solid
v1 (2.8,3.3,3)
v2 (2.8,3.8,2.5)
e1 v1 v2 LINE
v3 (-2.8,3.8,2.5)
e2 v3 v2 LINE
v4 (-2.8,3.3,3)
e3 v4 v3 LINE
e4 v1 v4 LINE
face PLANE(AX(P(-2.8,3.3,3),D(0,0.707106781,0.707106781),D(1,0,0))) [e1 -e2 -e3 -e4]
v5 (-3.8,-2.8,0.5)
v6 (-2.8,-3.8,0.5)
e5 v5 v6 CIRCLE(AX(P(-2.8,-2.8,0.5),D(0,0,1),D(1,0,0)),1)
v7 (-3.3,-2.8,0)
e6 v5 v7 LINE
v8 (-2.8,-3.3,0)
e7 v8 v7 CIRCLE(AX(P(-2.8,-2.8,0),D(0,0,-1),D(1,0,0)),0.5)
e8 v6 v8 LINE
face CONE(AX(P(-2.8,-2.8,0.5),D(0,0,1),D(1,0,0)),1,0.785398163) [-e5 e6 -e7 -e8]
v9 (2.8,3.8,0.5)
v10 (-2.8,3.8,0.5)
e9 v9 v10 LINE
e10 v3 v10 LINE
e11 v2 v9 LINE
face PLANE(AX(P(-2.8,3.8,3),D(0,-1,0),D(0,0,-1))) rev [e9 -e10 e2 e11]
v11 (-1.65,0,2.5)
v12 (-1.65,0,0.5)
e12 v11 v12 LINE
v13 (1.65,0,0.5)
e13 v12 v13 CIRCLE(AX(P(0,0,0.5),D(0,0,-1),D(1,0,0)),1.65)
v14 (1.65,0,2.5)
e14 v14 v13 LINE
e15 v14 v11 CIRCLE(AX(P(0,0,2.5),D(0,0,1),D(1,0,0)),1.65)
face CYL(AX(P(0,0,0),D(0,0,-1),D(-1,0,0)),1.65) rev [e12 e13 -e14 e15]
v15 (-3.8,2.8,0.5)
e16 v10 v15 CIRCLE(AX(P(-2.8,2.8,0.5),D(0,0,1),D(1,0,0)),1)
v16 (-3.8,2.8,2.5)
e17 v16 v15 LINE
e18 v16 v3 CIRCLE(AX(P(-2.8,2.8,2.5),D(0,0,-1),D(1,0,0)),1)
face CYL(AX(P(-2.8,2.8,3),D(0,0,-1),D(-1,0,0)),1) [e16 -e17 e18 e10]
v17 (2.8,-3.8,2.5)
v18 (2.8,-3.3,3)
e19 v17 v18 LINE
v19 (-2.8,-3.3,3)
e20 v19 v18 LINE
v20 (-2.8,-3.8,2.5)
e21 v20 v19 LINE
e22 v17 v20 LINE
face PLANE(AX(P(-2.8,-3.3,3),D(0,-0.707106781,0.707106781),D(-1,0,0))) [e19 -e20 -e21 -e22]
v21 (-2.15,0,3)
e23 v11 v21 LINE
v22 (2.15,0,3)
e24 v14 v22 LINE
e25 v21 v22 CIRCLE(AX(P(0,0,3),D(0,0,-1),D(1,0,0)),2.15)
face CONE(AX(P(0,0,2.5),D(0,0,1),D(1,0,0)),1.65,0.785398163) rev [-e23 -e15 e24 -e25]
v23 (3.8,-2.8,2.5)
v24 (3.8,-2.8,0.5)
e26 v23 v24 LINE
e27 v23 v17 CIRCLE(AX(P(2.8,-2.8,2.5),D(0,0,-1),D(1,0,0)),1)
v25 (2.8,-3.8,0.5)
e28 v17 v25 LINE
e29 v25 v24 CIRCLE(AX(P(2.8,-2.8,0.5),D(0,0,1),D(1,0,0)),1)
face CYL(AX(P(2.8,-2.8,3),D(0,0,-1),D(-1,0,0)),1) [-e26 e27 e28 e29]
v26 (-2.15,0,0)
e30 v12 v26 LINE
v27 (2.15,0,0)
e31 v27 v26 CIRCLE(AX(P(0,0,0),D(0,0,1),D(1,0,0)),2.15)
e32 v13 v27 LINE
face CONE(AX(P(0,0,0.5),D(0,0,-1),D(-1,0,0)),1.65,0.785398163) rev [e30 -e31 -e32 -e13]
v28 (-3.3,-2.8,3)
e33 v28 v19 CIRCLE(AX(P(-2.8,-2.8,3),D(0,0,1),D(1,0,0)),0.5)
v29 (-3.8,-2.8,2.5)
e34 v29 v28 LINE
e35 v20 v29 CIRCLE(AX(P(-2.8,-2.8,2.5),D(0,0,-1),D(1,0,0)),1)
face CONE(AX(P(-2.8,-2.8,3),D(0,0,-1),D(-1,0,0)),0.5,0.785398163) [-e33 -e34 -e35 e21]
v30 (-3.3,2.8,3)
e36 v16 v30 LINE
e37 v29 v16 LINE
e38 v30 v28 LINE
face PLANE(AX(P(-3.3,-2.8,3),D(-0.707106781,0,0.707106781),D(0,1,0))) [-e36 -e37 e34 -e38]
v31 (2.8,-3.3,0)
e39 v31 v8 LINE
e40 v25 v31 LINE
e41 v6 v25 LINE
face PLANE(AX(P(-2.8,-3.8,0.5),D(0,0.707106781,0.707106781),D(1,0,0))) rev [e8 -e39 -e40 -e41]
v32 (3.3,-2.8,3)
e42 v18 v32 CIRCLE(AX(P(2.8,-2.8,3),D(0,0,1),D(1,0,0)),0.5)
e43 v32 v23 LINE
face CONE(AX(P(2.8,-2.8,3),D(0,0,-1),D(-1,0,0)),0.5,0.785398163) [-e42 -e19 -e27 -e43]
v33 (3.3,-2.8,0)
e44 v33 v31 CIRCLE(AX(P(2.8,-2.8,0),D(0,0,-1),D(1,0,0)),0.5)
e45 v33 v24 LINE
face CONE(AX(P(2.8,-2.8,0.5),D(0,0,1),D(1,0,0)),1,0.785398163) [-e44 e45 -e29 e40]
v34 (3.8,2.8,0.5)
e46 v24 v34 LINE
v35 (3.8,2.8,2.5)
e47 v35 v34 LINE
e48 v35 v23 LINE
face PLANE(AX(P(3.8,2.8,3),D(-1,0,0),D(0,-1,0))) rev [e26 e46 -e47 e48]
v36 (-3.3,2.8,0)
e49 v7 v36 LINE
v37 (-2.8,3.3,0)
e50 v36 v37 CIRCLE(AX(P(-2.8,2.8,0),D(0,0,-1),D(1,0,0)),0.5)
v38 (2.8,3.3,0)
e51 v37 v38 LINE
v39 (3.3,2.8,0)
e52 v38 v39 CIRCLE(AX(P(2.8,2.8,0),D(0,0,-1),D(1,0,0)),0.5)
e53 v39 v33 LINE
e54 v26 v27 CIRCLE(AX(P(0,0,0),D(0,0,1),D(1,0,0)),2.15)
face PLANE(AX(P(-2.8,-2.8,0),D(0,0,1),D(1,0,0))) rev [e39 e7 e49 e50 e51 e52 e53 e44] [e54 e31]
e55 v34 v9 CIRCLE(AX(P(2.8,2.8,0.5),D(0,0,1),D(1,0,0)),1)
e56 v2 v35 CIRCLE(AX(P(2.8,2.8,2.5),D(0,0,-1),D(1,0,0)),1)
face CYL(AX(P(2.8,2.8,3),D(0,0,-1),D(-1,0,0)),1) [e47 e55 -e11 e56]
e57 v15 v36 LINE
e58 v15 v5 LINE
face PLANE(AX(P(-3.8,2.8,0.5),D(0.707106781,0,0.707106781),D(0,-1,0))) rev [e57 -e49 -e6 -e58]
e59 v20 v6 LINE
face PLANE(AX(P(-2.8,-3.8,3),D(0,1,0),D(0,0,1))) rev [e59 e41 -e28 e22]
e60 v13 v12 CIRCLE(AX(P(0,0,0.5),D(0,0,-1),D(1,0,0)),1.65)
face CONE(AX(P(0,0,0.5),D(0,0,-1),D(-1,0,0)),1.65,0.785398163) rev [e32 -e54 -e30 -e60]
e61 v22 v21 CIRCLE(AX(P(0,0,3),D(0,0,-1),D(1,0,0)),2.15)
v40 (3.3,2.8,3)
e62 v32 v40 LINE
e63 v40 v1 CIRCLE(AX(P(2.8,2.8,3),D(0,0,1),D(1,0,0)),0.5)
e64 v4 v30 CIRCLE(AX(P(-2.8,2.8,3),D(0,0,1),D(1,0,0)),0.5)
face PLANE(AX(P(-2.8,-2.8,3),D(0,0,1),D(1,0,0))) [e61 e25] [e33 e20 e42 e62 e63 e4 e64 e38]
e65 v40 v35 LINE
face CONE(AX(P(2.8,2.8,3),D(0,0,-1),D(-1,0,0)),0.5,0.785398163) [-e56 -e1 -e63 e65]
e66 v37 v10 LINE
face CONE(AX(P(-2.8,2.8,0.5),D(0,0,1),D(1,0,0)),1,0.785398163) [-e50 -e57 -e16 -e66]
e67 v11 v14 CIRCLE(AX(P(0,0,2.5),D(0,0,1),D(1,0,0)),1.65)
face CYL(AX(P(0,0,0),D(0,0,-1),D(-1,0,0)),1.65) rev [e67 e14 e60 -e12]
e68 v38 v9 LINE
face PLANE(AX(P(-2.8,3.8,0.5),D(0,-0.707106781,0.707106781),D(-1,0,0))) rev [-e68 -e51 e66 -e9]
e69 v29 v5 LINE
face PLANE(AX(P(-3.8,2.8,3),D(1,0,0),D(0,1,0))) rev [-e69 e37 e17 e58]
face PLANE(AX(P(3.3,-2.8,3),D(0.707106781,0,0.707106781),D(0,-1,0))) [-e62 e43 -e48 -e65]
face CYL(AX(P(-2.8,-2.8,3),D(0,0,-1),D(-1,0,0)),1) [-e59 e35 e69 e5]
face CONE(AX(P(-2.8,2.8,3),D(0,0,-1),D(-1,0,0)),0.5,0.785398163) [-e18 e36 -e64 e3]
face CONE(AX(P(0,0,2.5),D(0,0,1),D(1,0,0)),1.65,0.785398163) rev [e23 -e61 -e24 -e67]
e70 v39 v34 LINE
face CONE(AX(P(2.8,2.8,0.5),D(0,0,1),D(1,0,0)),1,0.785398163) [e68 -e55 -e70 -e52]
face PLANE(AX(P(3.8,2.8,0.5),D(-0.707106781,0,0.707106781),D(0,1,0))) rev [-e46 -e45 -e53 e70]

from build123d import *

# Parameters (mm, degrees)
SKETCH1_R             = 1.5
BOSS_EXTRUDE1_DEPTH   = 3
M4_TAPPED_HOLE1_D     = 3.3
M4_TAPPED_HOLE1_DEPTH = 11.5
M4_TAPPED_HOLE1_TIP   = 0.991420021
CHAMFER1_SIZE         = 0.5
CHAMFER2_SIZE         = 0.5
CHAMFER3_SIZE         = 0.5


with BuildPart() as part:
    # Sketch1 → Boss-Extrude1 (new body)
    with BuildSketch(Plane.XY):
        with BuildLine():
            Line((-2.8, 3.8), (2.8, 3.8))
            ThreePointArc((2.8, 3.8), (3.507106781, 3.507106781), (3.8, 2.8))
            Line((3.8, 2.8), (3.8, -2.8))
            ThreePointArc((3.8, -2.8), (3.507106781, -3.507106781), (2.8, -3.8))
            Line((2.8, -3.8), (-2.8, -3.8))
            ThreePointArc((-2.8, -3.8), (-3.507106781, -3.507106781), (-3.8, -2.8))
            Line((-3.8, -2.8), (-3.8, 2.8))
            ThreePointArc((-3.8, 2.8), (-3.507106781, 3.507106781), (-2.8, 3.8))
        make_face()
        Circle(SKETCH1_R, mode=Mode.SUBTRACT)
    extrude(amount=BOSS_EXTRUDE1_DEPTH)

    # M4 Tapped Hole1
    with Locations(Plane(origin=(0, 0, 0), x_dir=(-1, 0, 0), z_dir=(0, 0, -1))):
        with Locations((0, 0)):
            Hole(M4_TAPPED_HOLE1_D / 2, depth=M4_TAPPED_HOLE1_DEPTH)
            with Locations((0, 0, -(M4_TAPPED_HOLE1_DEPTH + M4_TAPPED_HOLE1_TIP / 2))):  # 118° drill point
                Cone(0, M4_TAPPED_HOLE1_D / 2, M4_TAPPED_HOLE1_TIP, mode=Mode.SUBTRACT)

    # Chamfer1
    chamfer1_edges = [part.edges().sort_by_distance(p)[0] for p in [
        (-1.65, 0, 0),
    ]]
    chamfer(chamfer1_edges, length=CHAMFER1_SIZE)

    # Chamfer2
    chamfer2_edges = [part.edges().sort_by_distance(p)[0] for p in [
        (-1.65, 0, 3),
    ]]
    chamfer(chamfer2_edges, length=CHAMFER2_SIZE)

    # Chamfer3
    chamfer3_edges = [part.edges().sort_by_distance(p)[0] for p in [
        (3.507106781, -3.507106781, 3),
        (0, -3.8, 0),
        (-3.507106781, -3.507106781, 0),
        (3.8, 0, 3),
        (3.507106781, 3.507106781, 3),
        (0, 3.8, 3),
        (-3.507106781, 3.507106781, 3),
        (-3.8, 0, 3),
        (-3.507106781, -3.507106781, 3),
        (0, -3.8, 3),
        (-3.8, 0, 0),
        (-3.507106781, 3.507106781, 0),
        (0, 3.8, 0),
        (3.507106781, 3.507106781, 0),
        (3.8, 0, 0),
        (3.507106781, -3.507106781, 0),
    ]]
    chamfer(chamfer3_edges, length=CHAMFER3_SIZE)


solid = part.part
